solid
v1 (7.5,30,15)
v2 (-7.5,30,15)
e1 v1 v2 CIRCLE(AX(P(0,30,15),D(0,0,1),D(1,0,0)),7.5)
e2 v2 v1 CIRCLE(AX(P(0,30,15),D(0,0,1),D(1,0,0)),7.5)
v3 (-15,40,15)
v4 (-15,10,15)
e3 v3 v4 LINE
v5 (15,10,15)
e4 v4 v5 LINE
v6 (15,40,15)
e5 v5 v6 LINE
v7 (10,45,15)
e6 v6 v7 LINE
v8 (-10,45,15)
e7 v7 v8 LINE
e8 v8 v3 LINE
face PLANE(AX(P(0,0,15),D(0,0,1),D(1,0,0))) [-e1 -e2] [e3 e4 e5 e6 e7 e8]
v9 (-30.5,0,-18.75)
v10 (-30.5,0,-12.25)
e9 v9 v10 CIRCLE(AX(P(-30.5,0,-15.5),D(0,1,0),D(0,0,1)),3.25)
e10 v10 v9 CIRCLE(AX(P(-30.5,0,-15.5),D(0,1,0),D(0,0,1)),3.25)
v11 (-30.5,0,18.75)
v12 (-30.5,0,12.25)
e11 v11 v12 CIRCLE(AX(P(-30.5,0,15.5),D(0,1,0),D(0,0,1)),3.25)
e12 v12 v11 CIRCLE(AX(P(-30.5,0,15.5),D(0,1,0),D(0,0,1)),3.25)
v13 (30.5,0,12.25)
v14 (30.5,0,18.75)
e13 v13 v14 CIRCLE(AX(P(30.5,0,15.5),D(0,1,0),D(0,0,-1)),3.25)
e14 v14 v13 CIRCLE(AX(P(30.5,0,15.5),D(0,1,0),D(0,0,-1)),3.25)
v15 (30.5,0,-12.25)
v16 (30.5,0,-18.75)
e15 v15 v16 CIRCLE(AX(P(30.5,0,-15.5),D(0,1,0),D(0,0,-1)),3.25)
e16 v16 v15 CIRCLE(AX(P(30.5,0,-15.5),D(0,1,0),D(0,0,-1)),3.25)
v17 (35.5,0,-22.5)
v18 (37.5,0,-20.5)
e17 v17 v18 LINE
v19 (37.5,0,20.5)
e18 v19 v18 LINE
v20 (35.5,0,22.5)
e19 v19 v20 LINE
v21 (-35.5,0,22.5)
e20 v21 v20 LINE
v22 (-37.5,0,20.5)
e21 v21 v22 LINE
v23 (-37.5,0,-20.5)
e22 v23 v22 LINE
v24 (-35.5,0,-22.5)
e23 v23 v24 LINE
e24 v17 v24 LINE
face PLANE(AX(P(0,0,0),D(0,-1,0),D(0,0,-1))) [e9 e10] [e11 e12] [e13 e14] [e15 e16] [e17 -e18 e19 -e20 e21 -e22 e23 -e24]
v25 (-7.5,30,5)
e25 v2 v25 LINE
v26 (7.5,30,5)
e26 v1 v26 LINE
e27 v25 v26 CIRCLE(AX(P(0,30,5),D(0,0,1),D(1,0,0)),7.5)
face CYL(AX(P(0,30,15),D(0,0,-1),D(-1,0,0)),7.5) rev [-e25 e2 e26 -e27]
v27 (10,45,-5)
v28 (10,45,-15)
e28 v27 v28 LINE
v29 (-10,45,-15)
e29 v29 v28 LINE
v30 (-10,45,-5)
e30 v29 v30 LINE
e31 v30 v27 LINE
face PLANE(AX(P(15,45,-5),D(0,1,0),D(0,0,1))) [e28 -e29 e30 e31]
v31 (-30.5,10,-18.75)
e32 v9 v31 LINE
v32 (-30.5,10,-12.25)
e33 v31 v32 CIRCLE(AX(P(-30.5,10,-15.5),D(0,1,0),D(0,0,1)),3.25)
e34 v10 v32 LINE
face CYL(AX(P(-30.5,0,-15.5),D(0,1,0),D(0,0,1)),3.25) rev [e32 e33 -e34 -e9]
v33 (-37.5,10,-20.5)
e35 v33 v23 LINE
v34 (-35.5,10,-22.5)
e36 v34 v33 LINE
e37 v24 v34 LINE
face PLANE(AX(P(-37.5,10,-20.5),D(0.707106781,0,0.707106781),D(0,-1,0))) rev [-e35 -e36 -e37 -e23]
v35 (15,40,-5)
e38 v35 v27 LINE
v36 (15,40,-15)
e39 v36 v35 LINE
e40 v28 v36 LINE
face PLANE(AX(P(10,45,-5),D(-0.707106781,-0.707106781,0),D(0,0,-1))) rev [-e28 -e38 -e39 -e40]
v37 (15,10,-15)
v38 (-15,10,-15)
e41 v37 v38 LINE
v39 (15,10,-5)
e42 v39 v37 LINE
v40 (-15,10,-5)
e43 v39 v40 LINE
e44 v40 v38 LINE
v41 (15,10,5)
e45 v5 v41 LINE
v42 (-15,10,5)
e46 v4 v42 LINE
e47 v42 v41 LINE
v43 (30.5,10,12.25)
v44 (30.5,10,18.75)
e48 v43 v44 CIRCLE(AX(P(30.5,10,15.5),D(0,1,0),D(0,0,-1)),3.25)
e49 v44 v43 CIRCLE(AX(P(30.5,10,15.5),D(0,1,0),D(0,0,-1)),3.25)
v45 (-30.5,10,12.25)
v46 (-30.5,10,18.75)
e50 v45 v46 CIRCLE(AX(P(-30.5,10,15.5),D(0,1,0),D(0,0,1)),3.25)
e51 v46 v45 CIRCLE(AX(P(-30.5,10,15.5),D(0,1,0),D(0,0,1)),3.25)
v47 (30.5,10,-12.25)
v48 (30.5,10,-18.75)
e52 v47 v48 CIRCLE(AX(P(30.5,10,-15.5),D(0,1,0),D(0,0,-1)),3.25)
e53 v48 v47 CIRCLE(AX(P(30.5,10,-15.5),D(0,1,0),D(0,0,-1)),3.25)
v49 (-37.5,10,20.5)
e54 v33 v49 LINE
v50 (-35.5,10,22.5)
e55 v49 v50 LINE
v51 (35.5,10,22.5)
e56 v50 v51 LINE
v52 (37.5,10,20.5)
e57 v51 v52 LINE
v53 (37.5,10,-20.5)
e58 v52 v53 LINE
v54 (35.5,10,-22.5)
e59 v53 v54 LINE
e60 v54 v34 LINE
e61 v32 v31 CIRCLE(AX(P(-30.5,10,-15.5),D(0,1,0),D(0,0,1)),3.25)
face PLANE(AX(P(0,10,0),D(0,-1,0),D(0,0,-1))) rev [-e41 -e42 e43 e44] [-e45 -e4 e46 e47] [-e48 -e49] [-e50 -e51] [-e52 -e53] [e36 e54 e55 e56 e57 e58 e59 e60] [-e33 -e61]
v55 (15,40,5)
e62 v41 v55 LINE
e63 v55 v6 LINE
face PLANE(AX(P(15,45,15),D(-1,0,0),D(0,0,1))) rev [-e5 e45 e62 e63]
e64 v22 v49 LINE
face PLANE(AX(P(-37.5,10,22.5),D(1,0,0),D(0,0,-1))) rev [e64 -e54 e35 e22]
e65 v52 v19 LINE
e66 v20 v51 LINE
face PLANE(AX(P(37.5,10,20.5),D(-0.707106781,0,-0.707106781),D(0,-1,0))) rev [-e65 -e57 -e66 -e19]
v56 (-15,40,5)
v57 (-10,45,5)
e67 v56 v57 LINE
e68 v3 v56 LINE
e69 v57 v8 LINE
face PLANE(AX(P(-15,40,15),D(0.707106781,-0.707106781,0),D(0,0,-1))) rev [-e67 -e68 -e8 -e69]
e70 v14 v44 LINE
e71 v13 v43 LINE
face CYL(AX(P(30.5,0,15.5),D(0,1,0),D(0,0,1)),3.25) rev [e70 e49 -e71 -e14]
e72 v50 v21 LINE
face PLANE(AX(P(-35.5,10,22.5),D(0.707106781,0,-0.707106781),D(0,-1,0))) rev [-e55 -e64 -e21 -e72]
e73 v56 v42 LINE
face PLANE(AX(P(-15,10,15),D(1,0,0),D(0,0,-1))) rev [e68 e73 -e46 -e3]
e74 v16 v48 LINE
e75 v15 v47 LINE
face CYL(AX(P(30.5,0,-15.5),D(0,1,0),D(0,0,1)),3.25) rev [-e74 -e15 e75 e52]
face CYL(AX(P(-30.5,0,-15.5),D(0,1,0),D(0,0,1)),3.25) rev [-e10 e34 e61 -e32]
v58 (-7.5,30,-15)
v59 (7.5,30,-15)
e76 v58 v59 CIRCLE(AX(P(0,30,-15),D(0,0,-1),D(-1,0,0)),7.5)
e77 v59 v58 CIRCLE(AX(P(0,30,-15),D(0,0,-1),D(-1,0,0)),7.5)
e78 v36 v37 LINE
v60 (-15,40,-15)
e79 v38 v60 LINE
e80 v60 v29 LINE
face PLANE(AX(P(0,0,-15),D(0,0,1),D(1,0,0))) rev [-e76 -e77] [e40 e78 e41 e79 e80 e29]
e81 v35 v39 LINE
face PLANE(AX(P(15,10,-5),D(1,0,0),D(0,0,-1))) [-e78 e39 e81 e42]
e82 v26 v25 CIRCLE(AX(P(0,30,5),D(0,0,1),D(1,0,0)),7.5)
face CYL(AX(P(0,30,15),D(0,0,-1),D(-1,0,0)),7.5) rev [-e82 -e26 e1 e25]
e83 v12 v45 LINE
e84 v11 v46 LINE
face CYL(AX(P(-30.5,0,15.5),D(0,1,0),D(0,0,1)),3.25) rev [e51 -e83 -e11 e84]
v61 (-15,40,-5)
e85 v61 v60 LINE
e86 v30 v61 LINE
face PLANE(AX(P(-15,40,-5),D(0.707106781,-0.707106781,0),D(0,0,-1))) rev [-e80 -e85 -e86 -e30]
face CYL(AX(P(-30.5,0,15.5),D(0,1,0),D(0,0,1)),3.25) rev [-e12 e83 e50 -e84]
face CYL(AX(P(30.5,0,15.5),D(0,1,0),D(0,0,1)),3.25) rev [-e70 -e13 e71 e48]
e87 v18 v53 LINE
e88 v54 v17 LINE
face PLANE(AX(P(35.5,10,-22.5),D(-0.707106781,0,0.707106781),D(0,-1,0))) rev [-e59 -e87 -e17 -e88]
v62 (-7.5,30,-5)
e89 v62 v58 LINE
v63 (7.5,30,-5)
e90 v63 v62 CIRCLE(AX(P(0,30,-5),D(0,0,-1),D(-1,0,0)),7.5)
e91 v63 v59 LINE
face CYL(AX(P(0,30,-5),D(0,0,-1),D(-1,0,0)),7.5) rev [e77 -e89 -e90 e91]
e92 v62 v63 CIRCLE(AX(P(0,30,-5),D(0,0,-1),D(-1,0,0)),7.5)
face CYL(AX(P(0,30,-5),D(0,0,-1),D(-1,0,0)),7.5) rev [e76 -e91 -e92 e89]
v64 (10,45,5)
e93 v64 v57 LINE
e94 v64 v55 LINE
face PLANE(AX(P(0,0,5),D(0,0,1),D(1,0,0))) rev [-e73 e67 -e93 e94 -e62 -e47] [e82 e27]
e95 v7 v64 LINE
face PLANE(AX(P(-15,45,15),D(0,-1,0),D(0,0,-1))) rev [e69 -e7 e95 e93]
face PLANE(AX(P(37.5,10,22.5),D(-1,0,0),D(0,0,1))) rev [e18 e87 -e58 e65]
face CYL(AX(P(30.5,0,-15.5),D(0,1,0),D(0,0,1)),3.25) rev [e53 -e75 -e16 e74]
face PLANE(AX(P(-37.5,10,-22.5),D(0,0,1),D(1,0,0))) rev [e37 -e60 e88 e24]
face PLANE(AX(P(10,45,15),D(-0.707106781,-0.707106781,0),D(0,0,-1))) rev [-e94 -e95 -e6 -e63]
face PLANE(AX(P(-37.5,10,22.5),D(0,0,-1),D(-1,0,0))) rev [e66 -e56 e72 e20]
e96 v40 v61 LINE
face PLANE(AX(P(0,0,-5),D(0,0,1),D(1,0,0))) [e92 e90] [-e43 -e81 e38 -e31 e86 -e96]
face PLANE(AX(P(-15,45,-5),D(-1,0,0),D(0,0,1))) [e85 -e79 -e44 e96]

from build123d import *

# Parameters (mm, degrees)
BASE_PLATE_SKETCH_W        = 75
BASE_PLATE_SKETCH_H        = 45
BASE_PLATE_75X45X10_DEPTH  = 10
BASE_CORNER_CHAMFER_1_SIZE = 2
BASE_CORNER_CHAMFER_2_SIZE = 2
BASE_CORNER_CHAMFER_3_SIZE = 2
BASE_CORNER_CHAMFER_4_SIZE = 2
FORK_BODY_SKETCH_W         = 30
FORK_BODY_SKETCH_H         = 35
FORK_BODY_SKETCH_R         = 7.5
FORK_BODY_DEPTH            = 10
FORK_EXTENSION_SKETCH_W    = 30
FORK_EXTENSION_SKETCH_H    = 35
FORK_EXTENSION_SKETCH_R    = 7.5
FORK_EXTENSION_DEPTH       = 17.5
FORK_SLOT_SKETCH_W         = 30
FORK_SLOT_SKETCH_H         = 35
FORK_SLOT_SKETCH_R         = 7.5
FORK_SLOT_DEPTH            = 7.5
FORK_TOP_CHAMFER_1_SIZE    = 5
FORK_TOP_CHAMFER_2_SIZE    = 5
MOUNTING_HOLES_SKETCH_R    = 3.25
MOUNTING_HOLES_DEPTH       = 57.013391256


with BuildPart() as part:
    # Base Plate Sketch → Base Plate 75x45x10 (new body)
    with BuildSketch(Plane(origin=(0, 0, 0), x_dir=(1, 0, 0), z_dir=(0, 1, 0))):
        Rectangle(BASE_PLATE_SKETCH_W, BASE_PLATE_SKETCH_H)
    extrude(amount=BASE_PLATE_75X45X10_DEPTH)

    # Base Corner Chamfer 1
    base_corner_chamfer_1_edges = [part.edges().sort_by_distance(p)[0] for p in [
        (37.5, 5, 22.5),
    ]]
    chamfer(base_corner_chamfer_1_edges, length=BASE_CORNER_CHAMFER_1_SIZE)

    # Base Corner Chamfer 2
    base_corner_chamfer_2_edges = [part.edges().sort_by_distance(p)[0] for p in [
        (-37.5, 5, 22.5),
    ]]
    chamfer(base_corner_chamfer_2_edges, length=BASE_CORNER_CHAMFER_2_SIZE)

    # Base Corner Chamfer 3
    base_corner_chamfer_3_edges = [part.edges().sort_by_distance(p)[0] for p in [
        (-37.5, 5, -22.5),
    ]]
    chamfer(base_corner_chamfer_3_edges, length=BASE_CORNER_CHAMFER_3_SIZE)

    # Base Corner Chamfer 4
    base_corner_chamfer_4_edges = [part.edges().sort_by_distance(p)[0] for p in [
        (37.5, 5, -22.5),
    ]]
    chamfer(base_corner_chamfer_4_edges, length=BASE_CORNER_CHAMFER_4_SIZE)

    # Fork Body Sketch → Fork Body (add)
    with BuildSketch(Plane.XY.offset(5)):
        with Locations((0, 27.5)):
            Rectangle(FORK_BODY_SKETCH_W, FORK_BODY_SKETCH_H)
        with Locations((0, 30)):
            Circle(FORK_BODY_SKETCH_R, mode=Mode.SUBTRACT)
    extrude(amount=FORK_BODY_DEPTH)

    # Fork Extension Sketch → Fork Extension (add)
    with BuildSketch(Plane(origin=(0, 0, -22.5), x_dir=(-1, 0, 0), z_dir=(0, 0, -1))):
        with Locations((0, 27.5)):
            Rectangle(FORK_EXTENSION_SKETCH_W, FORK_EXTENSION_SKETCH_H)
        with Locations(Location((0, 30, 0), (0, 0, 180))):
            Circle(FORK_EXTENSION_SKETCH_R, mode=Mode.SUBTRACT)
    extrude(amount=-FORK_EXTENSION_DEPTH)

    # Fork Slot Sketch → Fork Slot (cut)
    with BuildSketch(Plane(origin=(0, 0, -22.5), x_dir=(-1, 0, 0), z_dir=(0, 0, -1))):
        with Locations((0, 27.5)):
            Rectangle(FORK_SLOT_SKETCH_W, FORK_SLOT_SKETCH_H)
        with Locations(Location((0, 30, 0), (0, 0, 180))):
            Circle(FORK_SLOT_SKETCH_R, mode=Mode.SUBTRACT)
    extrude(amount=-FORK_SLOT_DEPTH, mode=Mode.SUBTRACT)

    # Fork Top Chamfer 1
    fork_top_chamfer_1_edges = [part.edges().sort_by_distance(p)[0] for p in [
        (-15, 45, -10),
    ]]
    chamfer(fork_top_chamfer_1_edges, length=FORK_TOP_CHAMFER_1_SIZE)

    # Fork Top Chamfer 2
    fork_top_chamfer_2_edges = [part.edges().sort_by_distance(p)[0] for p in [
        (15, 45, 10),
        (-15, 45, 10),
        (15, 45, -10),
    ]]
    chamfer(fork_top_chamfer_2_edges, length=FORK_TOP_CHAMFER_2_SIZE)

    # Mounting Holes Sketch → Mounting Holes (cut, through all)
    with BuildSketch(Plane(origin=(0, 10, 0), x_dir=(1, 0, 0), z_dir=(0, 1, 0))):
        with Locations(Location((-30.5, 15.5, 0), (0, 0, 270))):
            Circle(MOUNTING_HOLES_SKETCH_R)
        with Locations(Location((-30.5, -15.5, 0), (0, 0, 270))):
            Circle(MOUNTING_HOLES_SKETCH_R)
        with Locations(Location((30.5, -15.5, 0), (0, 0, 90))):
            Circle(MOUNTING_HOLES_SKETCH_R)
        with Locations(Location((30.5, 15.5, 0), (0, 0, 90))):
            Circle(MOUNTING_HOLES_SKETCH_R)
    extrude(amount=-MOUNTING_HOLES_DEPTH, mode=Mode.SUBTRACT)


solid = part.part
